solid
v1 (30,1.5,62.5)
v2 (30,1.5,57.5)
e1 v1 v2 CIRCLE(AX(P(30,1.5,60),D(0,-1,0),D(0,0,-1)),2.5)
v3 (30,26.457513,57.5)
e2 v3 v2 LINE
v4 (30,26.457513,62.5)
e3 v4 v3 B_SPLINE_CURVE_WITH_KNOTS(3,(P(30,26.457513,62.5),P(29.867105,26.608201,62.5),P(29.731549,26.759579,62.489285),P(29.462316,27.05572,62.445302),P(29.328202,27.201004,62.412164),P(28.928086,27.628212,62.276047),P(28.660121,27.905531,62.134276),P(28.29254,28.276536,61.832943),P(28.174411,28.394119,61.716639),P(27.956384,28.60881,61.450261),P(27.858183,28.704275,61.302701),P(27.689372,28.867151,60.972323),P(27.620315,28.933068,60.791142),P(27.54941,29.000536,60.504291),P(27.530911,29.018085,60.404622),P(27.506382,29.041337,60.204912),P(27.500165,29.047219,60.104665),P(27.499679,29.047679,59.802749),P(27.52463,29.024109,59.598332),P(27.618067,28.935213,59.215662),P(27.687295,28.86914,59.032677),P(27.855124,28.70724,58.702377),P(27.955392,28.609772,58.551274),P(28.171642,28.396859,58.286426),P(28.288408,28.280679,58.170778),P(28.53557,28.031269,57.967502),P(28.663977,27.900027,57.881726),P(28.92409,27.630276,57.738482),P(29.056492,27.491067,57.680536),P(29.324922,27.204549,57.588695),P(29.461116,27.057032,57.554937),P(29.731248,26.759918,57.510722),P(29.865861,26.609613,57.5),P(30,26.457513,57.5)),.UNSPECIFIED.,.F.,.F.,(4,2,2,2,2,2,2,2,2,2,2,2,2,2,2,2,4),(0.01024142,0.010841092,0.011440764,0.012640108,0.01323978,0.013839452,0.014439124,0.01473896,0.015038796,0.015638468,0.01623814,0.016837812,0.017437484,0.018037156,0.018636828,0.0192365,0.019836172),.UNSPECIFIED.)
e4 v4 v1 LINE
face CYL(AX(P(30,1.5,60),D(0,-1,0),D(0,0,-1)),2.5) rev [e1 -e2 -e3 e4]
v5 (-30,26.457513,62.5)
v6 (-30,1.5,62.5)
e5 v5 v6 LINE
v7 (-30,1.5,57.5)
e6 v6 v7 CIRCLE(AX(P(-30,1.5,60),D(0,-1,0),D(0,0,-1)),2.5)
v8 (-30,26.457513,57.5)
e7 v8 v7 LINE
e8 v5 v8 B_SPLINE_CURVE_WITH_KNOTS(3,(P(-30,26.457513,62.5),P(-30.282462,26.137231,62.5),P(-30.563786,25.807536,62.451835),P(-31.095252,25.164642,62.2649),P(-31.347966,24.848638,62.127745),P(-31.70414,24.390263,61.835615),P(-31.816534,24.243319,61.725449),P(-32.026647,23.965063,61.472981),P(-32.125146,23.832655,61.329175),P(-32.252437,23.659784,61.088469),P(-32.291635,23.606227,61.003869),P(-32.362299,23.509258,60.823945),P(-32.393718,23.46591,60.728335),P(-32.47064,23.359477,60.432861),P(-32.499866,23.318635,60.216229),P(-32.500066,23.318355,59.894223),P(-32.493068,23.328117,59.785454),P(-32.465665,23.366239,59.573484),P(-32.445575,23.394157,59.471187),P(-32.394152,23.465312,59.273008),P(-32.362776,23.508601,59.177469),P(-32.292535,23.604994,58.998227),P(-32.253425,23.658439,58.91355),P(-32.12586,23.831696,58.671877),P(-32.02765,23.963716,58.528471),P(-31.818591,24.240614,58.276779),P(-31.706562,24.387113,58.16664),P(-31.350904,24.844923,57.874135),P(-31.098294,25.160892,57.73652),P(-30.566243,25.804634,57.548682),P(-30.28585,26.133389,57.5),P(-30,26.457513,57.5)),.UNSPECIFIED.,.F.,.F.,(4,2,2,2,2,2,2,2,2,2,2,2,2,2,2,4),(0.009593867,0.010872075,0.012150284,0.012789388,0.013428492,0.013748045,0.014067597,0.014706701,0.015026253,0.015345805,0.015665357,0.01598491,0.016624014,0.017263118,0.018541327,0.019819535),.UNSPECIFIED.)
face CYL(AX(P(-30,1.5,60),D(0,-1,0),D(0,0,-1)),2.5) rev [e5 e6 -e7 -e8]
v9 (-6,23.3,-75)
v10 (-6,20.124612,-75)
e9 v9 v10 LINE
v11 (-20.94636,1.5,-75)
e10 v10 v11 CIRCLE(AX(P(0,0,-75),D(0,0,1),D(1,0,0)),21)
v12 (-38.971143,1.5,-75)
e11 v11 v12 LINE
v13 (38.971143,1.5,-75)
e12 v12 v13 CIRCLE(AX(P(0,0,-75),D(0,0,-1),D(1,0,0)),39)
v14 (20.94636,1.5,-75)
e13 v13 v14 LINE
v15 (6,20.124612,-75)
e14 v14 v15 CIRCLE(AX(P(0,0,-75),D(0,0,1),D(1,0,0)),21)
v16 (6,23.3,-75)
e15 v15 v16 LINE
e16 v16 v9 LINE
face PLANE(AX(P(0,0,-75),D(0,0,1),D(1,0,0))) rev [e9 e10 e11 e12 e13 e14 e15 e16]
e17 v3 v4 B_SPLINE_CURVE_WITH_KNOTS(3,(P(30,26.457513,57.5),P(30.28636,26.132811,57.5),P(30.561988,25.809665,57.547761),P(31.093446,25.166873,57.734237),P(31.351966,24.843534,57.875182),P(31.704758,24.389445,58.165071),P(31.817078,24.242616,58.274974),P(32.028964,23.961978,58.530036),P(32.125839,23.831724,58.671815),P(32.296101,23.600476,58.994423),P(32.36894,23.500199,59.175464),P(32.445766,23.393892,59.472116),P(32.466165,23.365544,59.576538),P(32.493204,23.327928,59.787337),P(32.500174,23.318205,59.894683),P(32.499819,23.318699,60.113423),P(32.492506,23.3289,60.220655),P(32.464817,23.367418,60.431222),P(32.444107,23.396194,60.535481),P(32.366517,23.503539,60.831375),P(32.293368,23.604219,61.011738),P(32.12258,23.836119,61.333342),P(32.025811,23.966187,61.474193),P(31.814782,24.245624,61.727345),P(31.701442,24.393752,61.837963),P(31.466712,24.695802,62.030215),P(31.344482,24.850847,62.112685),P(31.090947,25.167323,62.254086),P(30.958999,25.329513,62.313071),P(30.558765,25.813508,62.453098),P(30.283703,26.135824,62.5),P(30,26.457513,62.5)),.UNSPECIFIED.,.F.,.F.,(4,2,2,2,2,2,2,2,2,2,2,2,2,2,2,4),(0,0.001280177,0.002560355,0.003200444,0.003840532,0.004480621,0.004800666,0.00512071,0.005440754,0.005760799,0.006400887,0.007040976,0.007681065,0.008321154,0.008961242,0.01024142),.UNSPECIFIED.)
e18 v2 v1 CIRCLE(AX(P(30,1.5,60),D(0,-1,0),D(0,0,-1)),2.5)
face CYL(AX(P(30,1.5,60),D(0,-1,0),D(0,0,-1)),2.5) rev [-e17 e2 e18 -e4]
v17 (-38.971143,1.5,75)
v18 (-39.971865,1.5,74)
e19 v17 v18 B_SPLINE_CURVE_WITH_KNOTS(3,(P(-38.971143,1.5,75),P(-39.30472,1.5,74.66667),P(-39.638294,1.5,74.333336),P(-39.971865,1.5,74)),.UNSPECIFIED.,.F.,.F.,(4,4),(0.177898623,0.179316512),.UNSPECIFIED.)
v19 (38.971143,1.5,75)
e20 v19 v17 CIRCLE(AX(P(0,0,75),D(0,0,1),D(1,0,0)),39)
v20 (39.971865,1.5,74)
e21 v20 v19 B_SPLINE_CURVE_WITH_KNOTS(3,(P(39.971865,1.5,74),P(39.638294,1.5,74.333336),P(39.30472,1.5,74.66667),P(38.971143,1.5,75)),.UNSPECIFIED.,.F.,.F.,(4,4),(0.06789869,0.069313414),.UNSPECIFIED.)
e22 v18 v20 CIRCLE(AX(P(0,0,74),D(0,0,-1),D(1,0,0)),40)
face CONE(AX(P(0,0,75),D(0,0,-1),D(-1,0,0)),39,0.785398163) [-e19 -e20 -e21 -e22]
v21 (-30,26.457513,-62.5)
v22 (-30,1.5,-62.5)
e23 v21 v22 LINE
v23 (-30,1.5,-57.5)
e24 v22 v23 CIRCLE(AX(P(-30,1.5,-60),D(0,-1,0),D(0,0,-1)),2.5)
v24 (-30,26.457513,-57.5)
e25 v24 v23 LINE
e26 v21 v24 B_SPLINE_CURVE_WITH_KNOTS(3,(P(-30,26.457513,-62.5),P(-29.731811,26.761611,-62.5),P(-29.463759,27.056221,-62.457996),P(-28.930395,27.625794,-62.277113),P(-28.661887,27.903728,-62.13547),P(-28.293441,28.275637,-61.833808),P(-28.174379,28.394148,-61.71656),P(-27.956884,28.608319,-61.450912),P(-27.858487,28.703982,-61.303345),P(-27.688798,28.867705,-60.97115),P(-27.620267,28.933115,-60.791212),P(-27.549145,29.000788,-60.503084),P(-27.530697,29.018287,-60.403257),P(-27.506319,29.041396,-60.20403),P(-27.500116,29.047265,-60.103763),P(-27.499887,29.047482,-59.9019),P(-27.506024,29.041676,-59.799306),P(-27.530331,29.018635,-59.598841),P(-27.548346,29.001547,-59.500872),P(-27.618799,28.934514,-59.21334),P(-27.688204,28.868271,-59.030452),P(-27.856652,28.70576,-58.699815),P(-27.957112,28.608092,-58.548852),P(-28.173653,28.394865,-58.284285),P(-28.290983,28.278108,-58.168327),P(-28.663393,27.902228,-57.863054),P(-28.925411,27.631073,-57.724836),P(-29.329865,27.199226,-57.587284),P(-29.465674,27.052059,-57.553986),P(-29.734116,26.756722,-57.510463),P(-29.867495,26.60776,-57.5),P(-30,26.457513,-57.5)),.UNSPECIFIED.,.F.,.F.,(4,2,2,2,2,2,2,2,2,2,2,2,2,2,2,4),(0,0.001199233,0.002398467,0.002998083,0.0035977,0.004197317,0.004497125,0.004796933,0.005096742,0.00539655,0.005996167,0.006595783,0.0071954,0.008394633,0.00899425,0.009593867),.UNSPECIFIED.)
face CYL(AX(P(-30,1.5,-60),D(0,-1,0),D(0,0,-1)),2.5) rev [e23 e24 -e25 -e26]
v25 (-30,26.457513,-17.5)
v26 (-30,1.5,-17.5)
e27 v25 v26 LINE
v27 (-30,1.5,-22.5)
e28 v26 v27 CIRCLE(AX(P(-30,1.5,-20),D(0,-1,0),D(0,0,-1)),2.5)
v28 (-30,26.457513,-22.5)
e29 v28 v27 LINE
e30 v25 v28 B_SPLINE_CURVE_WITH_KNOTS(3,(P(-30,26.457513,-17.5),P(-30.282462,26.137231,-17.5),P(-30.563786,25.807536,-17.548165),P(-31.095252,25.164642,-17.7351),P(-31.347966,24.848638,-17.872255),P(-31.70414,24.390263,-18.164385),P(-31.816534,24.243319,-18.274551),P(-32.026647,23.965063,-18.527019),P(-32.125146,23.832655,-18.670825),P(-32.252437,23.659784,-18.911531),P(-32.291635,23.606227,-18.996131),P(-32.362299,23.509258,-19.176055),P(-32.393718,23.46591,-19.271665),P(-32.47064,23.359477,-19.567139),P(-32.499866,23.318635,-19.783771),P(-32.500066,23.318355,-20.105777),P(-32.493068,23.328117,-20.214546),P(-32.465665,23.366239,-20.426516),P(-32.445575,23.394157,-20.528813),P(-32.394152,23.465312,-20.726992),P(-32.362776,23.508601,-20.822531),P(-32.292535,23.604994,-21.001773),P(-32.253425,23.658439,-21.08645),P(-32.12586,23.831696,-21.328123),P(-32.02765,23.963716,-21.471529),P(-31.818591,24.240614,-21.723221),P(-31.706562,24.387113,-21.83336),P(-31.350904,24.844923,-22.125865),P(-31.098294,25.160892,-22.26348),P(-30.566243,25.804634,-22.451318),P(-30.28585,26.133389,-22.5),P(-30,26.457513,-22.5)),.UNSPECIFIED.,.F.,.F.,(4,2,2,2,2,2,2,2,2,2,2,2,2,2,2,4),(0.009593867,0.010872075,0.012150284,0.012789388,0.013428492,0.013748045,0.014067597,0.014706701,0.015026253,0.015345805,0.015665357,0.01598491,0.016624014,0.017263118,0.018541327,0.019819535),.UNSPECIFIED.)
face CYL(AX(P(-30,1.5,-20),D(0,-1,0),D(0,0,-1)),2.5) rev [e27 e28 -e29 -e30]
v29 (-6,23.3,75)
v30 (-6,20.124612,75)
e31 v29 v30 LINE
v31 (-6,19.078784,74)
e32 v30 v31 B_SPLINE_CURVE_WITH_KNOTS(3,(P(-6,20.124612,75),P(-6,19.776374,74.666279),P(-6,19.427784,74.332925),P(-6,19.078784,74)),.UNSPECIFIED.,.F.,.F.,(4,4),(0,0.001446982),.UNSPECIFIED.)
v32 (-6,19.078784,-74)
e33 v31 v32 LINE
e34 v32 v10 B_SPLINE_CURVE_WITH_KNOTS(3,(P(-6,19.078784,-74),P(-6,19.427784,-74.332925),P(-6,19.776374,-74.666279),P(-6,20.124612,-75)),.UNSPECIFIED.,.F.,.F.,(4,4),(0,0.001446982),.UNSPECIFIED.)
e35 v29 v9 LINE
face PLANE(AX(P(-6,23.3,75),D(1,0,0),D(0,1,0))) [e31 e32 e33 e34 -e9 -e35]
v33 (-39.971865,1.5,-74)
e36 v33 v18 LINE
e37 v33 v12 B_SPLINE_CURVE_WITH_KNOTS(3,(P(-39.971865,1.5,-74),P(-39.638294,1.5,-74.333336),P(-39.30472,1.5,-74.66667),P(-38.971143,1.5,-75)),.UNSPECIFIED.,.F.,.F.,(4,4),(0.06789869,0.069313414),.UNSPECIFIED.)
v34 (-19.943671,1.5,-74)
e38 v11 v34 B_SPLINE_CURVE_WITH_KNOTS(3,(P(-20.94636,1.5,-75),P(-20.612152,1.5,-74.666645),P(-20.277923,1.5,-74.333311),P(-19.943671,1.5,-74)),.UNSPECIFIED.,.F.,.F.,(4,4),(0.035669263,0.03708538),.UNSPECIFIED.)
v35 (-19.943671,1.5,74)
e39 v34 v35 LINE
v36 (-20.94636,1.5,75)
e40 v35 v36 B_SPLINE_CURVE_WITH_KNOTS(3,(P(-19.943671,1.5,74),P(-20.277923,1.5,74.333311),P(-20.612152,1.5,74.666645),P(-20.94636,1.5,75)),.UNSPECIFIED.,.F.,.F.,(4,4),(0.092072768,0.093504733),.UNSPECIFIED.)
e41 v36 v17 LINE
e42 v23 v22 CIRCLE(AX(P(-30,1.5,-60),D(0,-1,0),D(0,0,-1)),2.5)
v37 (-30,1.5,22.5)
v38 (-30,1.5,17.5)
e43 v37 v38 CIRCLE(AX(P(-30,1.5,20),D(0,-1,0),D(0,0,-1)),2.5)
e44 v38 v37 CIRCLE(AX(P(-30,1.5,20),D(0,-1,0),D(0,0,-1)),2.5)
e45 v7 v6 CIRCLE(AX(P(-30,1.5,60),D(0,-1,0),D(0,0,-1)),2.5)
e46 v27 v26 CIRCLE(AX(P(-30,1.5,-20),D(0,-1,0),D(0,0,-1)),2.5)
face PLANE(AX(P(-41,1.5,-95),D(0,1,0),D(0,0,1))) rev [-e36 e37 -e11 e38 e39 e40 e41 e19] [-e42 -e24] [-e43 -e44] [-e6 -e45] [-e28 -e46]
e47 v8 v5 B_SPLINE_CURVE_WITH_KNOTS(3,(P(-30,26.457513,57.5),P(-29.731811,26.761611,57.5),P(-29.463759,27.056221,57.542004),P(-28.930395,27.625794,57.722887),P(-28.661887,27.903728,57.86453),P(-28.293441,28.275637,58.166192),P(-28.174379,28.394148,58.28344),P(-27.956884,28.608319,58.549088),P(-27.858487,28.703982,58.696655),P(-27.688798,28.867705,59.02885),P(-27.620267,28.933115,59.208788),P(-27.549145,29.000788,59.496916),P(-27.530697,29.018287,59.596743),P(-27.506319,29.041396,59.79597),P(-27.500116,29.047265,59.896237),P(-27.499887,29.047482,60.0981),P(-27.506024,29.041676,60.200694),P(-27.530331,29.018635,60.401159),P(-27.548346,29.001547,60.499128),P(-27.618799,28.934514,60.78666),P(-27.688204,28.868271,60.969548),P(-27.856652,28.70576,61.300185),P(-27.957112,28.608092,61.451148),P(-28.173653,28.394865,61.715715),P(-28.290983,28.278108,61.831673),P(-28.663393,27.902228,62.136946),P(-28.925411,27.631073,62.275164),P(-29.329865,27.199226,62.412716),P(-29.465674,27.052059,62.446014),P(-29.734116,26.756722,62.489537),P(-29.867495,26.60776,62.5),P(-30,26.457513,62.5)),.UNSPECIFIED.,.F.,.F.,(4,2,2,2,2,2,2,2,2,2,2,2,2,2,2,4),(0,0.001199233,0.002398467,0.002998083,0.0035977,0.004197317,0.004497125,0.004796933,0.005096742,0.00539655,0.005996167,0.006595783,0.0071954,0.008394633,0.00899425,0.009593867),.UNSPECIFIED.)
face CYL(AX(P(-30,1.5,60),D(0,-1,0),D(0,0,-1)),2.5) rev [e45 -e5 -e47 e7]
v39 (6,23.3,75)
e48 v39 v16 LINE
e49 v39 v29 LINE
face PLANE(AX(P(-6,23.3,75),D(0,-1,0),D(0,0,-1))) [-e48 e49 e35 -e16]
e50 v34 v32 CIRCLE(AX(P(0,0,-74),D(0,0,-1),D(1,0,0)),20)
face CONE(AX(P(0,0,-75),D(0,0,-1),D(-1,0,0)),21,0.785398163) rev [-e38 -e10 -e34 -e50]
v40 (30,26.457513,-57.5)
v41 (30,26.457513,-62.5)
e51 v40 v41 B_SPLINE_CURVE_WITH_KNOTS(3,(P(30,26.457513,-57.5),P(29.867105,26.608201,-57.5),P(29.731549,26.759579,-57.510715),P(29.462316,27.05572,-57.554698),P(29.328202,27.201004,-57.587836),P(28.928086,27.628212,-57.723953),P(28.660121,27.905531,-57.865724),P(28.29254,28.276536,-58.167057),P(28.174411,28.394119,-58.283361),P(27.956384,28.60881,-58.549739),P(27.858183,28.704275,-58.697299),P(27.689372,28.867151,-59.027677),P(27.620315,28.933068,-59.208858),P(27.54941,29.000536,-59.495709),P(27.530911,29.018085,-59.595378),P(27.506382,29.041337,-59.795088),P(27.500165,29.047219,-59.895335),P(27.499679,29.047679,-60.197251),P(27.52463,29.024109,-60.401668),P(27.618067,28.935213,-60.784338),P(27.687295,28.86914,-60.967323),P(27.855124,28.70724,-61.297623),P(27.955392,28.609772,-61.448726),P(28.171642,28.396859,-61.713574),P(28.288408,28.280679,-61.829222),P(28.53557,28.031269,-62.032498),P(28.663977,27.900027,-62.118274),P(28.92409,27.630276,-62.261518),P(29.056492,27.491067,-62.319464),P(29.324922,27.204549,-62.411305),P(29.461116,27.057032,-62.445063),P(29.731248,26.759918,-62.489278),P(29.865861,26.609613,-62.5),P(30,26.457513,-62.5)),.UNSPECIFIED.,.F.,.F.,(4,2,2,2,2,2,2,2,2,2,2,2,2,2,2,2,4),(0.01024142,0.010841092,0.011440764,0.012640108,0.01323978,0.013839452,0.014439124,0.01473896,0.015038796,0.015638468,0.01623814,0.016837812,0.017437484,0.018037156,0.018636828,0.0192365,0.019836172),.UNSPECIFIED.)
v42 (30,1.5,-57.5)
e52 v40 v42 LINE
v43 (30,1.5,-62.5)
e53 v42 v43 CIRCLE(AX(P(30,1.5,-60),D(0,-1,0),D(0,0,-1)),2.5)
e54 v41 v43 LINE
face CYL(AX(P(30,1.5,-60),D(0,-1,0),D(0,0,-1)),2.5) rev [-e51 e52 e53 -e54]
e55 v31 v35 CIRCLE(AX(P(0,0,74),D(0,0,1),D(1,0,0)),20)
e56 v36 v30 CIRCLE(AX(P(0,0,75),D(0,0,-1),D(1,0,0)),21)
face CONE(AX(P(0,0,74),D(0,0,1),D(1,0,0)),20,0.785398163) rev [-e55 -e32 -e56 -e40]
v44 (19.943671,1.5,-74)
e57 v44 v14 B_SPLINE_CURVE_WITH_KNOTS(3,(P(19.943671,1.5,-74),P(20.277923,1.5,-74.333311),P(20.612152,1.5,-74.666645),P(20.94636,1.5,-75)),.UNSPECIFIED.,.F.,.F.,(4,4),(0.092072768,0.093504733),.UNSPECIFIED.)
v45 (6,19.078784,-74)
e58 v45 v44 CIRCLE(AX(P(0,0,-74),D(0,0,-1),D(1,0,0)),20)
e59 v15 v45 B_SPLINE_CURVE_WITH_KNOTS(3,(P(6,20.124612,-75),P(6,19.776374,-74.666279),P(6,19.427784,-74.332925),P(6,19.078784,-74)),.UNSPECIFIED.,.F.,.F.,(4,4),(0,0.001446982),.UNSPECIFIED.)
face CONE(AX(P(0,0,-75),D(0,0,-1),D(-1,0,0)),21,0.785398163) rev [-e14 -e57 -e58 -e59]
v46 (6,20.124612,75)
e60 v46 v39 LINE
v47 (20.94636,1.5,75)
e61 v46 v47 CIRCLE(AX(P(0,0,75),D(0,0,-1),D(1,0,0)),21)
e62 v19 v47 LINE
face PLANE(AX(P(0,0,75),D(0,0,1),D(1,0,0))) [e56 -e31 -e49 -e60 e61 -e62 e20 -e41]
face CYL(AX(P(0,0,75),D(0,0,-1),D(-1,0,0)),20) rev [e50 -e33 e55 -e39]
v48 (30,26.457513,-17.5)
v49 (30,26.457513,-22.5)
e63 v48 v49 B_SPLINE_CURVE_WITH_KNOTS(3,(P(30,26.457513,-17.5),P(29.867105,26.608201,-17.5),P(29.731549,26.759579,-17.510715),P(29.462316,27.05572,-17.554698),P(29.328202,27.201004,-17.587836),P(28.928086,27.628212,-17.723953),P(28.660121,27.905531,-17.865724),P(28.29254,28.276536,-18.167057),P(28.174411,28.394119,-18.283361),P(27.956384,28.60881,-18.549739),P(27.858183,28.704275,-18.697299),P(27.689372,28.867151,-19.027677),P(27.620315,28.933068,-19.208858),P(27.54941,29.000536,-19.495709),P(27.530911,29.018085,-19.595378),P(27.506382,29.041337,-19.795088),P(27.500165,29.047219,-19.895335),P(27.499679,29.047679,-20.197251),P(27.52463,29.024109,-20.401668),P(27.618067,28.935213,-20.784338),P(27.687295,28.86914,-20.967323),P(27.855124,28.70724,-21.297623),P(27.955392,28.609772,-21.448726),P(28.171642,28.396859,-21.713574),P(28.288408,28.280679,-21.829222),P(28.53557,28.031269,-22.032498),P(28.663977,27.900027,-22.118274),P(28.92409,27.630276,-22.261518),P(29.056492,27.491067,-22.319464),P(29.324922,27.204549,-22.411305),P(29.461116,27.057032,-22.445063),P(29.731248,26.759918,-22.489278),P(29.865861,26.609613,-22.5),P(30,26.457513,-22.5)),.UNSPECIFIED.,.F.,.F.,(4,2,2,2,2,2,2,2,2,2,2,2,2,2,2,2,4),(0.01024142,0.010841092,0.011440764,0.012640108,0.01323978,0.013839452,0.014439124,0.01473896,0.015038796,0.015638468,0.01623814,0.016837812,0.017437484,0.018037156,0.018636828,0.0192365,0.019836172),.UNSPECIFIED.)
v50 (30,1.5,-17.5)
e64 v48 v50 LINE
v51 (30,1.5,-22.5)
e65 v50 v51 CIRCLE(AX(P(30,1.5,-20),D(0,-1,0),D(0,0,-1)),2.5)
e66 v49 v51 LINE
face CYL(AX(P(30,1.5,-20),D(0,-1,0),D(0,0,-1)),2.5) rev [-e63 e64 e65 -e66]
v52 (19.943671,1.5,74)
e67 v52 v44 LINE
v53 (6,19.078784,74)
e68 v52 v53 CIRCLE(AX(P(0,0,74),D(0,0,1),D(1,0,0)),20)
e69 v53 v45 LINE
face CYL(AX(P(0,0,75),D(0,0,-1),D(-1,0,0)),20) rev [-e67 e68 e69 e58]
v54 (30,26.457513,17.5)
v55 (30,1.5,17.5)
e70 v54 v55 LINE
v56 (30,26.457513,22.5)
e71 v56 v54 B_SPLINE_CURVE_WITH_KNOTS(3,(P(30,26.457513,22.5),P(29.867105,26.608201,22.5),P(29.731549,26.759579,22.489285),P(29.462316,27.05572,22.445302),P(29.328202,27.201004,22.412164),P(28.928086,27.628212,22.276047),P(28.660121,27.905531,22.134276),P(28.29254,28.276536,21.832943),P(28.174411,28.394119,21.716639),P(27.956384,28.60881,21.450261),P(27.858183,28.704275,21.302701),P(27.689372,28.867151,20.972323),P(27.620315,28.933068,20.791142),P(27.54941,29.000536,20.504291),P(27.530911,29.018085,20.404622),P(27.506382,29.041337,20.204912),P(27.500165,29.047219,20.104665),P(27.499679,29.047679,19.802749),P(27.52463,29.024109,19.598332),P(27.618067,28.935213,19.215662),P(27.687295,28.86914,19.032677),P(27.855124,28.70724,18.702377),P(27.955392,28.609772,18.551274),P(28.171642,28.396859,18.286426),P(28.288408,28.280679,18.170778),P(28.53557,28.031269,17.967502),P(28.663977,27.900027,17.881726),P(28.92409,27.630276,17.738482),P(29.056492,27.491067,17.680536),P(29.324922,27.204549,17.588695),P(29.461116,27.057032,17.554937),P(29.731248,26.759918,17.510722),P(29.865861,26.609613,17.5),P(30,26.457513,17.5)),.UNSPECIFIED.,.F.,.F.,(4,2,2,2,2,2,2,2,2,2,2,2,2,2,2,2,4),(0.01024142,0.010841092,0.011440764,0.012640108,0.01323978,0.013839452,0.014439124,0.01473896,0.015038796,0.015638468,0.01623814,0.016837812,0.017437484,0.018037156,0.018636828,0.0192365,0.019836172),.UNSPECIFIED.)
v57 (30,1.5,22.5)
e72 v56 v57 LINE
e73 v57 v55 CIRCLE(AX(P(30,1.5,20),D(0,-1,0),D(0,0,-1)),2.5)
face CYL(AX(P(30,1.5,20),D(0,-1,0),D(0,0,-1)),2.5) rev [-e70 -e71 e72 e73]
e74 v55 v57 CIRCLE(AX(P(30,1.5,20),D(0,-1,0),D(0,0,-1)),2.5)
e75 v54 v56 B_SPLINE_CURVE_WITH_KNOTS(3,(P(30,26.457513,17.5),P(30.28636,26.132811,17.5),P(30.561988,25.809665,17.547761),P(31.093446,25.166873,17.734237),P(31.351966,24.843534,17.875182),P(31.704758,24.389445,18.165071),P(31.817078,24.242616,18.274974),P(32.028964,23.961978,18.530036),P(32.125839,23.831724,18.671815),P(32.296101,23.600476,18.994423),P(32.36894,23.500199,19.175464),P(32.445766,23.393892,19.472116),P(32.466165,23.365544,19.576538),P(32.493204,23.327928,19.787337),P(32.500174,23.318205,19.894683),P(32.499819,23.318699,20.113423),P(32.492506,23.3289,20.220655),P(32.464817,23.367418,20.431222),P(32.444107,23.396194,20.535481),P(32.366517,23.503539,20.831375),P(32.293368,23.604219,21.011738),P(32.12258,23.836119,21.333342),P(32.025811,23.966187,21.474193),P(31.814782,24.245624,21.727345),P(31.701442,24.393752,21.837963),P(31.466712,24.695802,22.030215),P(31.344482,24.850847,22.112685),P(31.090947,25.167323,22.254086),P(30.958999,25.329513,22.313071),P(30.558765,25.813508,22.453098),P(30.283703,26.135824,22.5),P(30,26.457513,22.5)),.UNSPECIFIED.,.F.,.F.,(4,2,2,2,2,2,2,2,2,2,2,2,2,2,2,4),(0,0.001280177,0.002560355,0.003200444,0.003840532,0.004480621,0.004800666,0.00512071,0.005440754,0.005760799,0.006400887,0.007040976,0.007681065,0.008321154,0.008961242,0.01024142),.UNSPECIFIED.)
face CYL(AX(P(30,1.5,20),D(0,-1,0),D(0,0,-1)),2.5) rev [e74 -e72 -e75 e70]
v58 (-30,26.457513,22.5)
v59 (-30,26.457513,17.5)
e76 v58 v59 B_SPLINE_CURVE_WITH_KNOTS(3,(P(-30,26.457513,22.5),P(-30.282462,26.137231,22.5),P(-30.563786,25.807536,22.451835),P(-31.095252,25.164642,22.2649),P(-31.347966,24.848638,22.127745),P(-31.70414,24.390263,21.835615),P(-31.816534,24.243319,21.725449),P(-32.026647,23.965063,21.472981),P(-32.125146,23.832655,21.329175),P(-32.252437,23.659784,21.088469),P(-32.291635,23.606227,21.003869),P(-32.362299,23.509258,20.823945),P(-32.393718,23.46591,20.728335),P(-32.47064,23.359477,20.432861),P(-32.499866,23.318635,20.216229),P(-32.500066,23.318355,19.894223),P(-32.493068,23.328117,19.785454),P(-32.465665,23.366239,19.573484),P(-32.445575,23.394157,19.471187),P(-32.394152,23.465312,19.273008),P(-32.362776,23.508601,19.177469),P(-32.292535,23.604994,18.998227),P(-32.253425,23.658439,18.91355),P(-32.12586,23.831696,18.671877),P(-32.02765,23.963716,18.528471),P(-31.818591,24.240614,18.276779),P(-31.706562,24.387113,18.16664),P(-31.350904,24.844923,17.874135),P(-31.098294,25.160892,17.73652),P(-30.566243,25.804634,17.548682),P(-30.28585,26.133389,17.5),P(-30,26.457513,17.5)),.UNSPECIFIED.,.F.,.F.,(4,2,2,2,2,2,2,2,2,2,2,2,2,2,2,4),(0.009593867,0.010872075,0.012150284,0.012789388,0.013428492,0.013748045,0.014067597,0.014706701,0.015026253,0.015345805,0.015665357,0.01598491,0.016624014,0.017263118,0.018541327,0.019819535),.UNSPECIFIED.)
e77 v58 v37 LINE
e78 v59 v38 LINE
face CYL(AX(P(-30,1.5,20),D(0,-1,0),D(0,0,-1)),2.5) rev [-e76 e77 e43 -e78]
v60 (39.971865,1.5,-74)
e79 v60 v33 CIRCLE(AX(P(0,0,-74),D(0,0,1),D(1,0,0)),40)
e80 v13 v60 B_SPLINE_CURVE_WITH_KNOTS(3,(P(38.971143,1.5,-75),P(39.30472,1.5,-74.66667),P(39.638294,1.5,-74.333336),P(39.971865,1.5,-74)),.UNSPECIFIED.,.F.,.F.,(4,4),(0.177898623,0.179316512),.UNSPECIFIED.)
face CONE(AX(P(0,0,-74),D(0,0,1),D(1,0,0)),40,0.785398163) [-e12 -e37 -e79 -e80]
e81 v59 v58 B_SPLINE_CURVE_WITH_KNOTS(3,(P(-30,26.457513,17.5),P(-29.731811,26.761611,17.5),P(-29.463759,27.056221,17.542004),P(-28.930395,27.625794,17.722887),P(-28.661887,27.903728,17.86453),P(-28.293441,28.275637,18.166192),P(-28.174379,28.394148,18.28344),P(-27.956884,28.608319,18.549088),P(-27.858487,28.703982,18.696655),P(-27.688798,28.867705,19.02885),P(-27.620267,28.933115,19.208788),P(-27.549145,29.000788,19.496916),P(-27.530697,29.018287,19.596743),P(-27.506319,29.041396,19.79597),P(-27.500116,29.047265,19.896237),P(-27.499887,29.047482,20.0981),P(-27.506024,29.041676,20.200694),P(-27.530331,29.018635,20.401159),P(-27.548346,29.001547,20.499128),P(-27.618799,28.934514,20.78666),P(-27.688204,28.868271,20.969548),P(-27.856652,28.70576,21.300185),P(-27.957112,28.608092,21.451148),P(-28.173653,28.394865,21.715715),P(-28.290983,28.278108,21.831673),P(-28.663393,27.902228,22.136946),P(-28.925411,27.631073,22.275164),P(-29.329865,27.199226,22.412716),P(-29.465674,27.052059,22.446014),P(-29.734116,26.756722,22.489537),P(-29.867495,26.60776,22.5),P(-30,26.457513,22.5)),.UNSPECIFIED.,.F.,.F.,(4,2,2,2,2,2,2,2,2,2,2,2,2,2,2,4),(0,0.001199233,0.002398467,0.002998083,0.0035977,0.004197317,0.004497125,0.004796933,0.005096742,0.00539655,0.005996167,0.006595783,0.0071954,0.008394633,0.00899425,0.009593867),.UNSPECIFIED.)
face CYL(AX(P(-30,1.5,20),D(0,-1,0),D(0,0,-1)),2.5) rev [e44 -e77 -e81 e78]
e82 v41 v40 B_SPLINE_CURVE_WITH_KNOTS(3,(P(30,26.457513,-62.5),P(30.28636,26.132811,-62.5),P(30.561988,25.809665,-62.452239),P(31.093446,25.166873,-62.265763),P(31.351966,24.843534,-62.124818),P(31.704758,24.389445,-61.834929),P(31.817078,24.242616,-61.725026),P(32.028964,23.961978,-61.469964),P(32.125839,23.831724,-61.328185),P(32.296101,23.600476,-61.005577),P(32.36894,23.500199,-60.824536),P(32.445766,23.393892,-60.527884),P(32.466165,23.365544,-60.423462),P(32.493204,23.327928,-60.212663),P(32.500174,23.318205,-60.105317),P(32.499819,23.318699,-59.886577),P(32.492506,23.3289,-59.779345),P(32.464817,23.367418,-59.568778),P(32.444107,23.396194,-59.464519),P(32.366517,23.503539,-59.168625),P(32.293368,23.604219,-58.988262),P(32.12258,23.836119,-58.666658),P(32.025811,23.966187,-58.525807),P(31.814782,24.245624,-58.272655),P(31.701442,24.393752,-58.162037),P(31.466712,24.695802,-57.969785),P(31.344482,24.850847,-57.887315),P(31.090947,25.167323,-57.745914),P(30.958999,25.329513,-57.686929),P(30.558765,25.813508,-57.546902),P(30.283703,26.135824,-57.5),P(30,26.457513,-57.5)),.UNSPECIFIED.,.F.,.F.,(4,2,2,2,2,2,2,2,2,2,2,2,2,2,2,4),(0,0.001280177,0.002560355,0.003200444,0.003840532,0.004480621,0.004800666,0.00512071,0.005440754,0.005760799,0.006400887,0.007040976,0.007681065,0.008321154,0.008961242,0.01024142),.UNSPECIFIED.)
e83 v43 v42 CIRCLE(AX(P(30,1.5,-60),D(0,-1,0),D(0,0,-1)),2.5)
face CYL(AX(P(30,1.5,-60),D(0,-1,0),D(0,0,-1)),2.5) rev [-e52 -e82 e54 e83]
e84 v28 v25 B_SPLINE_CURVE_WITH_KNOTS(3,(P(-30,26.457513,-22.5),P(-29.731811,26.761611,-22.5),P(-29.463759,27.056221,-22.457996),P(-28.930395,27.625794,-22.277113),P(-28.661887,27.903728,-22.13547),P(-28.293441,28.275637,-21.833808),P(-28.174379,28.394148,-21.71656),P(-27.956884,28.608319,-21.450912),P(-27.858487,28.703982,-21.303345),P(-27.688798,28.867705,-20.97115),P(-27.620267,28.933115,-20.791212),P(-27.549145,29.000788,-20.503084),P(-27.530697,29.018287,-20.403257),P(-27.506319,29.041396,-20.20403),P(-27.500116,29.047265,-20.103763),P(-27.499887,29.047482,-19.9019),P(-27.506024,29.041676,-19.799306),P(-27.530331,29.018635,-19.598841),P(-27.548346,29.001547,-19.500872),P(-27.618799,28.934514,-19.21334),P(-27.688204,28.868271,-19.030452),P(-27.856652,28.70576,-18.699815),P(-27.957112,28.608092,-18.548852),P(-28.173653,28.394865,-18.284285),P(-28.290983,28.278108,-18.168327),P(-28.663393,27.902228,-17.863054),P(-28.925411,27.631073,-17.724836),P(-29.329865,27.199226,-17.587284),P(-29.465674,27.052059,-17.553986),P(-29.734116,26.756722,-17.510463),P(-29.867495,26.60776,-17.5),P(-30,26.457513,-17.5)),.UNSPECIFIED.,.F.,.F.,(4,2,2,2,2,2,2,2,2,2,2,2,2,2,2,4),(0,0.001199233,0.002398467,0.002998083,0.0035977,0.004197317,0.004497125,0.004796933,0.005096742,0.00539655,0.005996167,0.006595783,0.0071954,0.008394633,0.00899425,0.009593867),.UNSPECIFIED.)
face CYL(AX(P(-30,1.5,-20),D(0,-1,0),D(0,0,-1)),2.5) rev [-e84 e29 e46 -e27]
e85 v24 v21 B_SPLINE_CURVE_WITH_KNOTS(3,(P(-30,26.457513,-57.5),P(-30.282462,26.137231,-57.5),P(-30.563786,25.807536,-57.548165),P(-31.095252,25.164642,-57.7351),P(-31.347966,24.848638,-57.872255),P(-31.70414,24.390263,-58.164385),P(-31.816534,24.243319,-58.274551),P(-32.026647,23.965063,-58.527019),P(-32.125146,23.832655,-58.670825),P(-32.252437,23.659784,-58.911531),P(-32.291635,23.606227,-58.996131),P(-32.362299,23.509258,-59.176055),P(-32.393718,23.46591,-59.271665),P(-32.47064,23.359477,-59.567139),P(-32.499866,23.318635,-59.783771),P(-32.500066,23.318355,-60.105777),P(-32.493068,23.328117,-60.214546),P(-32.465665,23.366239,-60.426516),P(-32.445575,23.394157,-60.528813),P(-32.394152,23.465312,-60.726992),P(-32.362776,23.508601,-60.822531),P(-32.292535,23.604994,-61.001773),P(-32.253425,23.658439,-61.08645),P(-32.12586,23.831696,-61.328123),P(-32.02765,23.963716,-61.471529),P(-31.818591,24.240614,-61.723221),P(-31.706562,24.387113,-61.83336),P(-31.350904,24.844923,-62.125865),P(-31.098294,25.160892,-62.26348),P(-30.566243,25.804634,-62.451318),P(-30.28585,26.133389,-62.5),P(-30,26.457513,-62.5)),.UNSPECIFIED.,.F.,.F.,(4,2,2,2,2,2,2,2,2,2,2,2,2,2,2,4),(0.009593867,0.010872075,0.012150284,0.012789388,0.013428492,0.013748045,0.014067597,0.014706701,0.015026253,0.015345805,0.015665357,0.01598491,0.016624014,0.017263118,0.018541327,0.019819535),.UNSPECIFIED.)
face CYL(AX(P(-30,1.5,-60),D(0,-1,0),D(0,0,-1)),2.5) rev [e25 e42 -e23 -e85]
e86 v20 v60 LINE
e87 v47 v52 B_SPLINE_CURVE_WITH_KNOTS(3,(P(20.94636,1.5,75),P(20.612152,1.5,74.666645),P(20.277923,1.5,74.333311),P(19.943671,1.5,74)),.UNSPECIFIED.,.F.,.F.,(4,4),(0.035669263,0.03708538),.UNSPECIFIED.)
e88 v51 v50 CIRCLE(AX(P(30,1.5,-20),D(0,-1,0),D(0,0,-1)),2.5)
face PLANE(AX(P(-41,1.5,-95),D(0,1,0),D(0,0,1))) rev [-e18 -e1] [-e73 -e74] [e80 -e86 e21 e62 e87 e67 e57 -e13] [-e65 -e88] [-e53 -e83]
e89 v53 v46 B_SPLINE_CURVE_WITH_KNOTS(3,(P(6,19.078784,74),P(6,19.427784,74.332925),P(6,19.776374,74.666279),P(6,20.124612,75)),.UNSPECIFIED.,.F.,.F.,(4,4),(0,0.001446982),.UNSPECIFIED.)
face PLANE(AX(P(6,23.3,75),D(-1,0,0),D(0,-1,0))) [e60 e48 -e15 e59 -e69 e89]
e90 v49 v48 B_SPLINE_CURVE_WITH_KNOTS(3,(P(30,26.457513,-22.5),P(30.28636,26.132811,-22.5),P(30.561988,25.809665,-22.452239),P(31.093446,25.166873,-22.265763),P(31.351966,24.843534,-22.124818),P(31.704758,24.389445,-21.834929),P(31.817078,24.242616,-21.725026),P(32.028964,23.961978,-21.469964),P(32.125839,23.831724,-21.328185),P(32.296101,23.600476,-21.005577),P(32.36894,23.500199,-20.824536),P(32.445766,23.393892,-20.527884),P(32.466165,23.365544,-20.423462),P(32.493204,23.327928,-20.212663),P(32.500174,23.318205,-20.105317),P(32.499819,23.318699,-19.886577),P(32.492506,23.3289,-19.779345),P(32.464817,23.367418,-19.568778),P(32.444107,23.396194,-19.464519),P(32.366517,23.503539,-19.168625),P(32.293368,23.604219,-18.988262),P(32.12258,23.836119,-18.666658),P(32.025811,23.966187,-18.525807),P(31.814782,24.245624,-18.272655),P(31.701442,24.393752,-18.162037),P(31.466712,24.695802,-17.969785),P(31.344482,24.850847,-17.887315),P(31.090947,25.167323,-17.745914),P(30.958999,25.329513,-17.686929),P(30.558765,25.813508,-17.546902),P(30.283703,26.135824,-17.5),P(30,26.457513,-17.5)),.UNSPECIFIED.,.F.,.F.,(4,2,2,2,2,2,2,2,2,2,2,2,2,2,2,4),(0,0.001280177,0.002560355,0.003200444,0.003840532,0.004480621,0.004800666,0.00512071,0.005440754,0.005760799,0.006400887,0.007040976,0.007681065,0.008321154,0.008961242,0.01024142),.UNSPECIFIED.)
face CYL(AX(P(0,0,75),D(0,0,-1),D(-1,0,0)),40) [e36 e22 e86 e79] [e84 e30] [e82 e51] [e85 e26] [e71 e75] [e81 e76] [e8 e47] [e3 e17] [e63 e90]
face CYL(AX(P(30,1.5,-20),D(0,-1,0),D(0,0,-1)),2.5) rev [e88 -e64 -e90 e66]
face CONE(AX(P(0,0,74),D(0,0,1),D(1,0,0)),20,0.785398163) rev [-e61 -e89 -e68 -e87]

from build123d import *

# Parameters (mm, degrees)
SKETCH1_R            = 40
BOSS_EXTRUDE1_DEPTH  = 75
CHAMFER1_SIZE        = 1
SKETCH2_W            = 82
SKETCH2_H            = 3
CUT_EXTRUDE1_DEPTH   = 170
LPATTERN1_COUNT      = 4
LPATTERN1_PITCH      = 40
LPATTERN1_COUNT_DIR2 = 2
LPATTERN1_PITCH_DIR2 = 60


with BuildPart() as part:
    # Sketch1 → Boss-Extrude1 (new, symmetric)
    with BuildSketch(Plane.XY):
        Circle(SKETCH1_R)
        with BuildLine():
            Line((-6, 23.3), (6, 23.3))
            Line((6, 23.3), (6, 19.078784028))
            ThreePointArc((6, 19.078784028), (0, -20), (-6, 19.078784028))
            Line((-6, 19.078784028), (-6, 23.3))
        make_face(mode=Mode.SUBTRACT)
    extrude(amount=BOSS_EXTRUDE1_DEPTH, both=True)

    # Chamfer1
    chamfer1_edges = [part.edges().sort_by_distance(p)[0] for p in [
        (-40, 0, -75),
        (-40, 0, 75),
        (0, -20, -75),
        (0, -20, 75),
    ]]
    chamfer(chamfer1_edges, length=CHAMFER1_SIZE)

    # Sketch2 → Cut-Extrude1 (cut)
    with BuildSketch(Plane.XY.offset(75)):
        Rectangle(SKETCH2_W, SKETCH2_H)
    extrude(amount=-CUT_EXTRUDE1_DEPTH, mode=Mode.SUBTRACT)


with BuildPart() as cut_extrude1_kept_piece:
    # of the separate pieces the step leaves, the one the design keeps (cut_extrude1_pieces_kept)
    add(part.part.solids().sort_by_distance((39.971865105, 1.5, -74))[0])

    # Sketch5 → M6 Tapped Hole1 (revolve, cut)
    with BuildSketch(Plane(origin=(30, 1.5, 60), x_dir=(0, 0, -1), z_dir=(1, 0, 0))):
        Polygon((0, 0), (0, 40.502151548), (2.5, 39), (2.5, 0), align=None)
    m6_tapped_hole1 = revolve(axis=Axis((30, -4.85, 60), (0, 1, 0)), mode=Mode.SUBTRACT)

    # LPattern1: M6 Tapped Hole1 4 × 2
    with Locations(*[(-j * LPATTERN1_PITCH_DIR2, 0, -i * LPATTERN1_PITCH) for i in range(LPATTERN1_COUNT) for j in range(LPATTERN1_COUNT_DIR2) if (i, j) != (0, 0)]):
        add(m6_tapped_hole1, mode=Mode.SUBTRACT)


solid = cut_extrude1_kept_piece.part
